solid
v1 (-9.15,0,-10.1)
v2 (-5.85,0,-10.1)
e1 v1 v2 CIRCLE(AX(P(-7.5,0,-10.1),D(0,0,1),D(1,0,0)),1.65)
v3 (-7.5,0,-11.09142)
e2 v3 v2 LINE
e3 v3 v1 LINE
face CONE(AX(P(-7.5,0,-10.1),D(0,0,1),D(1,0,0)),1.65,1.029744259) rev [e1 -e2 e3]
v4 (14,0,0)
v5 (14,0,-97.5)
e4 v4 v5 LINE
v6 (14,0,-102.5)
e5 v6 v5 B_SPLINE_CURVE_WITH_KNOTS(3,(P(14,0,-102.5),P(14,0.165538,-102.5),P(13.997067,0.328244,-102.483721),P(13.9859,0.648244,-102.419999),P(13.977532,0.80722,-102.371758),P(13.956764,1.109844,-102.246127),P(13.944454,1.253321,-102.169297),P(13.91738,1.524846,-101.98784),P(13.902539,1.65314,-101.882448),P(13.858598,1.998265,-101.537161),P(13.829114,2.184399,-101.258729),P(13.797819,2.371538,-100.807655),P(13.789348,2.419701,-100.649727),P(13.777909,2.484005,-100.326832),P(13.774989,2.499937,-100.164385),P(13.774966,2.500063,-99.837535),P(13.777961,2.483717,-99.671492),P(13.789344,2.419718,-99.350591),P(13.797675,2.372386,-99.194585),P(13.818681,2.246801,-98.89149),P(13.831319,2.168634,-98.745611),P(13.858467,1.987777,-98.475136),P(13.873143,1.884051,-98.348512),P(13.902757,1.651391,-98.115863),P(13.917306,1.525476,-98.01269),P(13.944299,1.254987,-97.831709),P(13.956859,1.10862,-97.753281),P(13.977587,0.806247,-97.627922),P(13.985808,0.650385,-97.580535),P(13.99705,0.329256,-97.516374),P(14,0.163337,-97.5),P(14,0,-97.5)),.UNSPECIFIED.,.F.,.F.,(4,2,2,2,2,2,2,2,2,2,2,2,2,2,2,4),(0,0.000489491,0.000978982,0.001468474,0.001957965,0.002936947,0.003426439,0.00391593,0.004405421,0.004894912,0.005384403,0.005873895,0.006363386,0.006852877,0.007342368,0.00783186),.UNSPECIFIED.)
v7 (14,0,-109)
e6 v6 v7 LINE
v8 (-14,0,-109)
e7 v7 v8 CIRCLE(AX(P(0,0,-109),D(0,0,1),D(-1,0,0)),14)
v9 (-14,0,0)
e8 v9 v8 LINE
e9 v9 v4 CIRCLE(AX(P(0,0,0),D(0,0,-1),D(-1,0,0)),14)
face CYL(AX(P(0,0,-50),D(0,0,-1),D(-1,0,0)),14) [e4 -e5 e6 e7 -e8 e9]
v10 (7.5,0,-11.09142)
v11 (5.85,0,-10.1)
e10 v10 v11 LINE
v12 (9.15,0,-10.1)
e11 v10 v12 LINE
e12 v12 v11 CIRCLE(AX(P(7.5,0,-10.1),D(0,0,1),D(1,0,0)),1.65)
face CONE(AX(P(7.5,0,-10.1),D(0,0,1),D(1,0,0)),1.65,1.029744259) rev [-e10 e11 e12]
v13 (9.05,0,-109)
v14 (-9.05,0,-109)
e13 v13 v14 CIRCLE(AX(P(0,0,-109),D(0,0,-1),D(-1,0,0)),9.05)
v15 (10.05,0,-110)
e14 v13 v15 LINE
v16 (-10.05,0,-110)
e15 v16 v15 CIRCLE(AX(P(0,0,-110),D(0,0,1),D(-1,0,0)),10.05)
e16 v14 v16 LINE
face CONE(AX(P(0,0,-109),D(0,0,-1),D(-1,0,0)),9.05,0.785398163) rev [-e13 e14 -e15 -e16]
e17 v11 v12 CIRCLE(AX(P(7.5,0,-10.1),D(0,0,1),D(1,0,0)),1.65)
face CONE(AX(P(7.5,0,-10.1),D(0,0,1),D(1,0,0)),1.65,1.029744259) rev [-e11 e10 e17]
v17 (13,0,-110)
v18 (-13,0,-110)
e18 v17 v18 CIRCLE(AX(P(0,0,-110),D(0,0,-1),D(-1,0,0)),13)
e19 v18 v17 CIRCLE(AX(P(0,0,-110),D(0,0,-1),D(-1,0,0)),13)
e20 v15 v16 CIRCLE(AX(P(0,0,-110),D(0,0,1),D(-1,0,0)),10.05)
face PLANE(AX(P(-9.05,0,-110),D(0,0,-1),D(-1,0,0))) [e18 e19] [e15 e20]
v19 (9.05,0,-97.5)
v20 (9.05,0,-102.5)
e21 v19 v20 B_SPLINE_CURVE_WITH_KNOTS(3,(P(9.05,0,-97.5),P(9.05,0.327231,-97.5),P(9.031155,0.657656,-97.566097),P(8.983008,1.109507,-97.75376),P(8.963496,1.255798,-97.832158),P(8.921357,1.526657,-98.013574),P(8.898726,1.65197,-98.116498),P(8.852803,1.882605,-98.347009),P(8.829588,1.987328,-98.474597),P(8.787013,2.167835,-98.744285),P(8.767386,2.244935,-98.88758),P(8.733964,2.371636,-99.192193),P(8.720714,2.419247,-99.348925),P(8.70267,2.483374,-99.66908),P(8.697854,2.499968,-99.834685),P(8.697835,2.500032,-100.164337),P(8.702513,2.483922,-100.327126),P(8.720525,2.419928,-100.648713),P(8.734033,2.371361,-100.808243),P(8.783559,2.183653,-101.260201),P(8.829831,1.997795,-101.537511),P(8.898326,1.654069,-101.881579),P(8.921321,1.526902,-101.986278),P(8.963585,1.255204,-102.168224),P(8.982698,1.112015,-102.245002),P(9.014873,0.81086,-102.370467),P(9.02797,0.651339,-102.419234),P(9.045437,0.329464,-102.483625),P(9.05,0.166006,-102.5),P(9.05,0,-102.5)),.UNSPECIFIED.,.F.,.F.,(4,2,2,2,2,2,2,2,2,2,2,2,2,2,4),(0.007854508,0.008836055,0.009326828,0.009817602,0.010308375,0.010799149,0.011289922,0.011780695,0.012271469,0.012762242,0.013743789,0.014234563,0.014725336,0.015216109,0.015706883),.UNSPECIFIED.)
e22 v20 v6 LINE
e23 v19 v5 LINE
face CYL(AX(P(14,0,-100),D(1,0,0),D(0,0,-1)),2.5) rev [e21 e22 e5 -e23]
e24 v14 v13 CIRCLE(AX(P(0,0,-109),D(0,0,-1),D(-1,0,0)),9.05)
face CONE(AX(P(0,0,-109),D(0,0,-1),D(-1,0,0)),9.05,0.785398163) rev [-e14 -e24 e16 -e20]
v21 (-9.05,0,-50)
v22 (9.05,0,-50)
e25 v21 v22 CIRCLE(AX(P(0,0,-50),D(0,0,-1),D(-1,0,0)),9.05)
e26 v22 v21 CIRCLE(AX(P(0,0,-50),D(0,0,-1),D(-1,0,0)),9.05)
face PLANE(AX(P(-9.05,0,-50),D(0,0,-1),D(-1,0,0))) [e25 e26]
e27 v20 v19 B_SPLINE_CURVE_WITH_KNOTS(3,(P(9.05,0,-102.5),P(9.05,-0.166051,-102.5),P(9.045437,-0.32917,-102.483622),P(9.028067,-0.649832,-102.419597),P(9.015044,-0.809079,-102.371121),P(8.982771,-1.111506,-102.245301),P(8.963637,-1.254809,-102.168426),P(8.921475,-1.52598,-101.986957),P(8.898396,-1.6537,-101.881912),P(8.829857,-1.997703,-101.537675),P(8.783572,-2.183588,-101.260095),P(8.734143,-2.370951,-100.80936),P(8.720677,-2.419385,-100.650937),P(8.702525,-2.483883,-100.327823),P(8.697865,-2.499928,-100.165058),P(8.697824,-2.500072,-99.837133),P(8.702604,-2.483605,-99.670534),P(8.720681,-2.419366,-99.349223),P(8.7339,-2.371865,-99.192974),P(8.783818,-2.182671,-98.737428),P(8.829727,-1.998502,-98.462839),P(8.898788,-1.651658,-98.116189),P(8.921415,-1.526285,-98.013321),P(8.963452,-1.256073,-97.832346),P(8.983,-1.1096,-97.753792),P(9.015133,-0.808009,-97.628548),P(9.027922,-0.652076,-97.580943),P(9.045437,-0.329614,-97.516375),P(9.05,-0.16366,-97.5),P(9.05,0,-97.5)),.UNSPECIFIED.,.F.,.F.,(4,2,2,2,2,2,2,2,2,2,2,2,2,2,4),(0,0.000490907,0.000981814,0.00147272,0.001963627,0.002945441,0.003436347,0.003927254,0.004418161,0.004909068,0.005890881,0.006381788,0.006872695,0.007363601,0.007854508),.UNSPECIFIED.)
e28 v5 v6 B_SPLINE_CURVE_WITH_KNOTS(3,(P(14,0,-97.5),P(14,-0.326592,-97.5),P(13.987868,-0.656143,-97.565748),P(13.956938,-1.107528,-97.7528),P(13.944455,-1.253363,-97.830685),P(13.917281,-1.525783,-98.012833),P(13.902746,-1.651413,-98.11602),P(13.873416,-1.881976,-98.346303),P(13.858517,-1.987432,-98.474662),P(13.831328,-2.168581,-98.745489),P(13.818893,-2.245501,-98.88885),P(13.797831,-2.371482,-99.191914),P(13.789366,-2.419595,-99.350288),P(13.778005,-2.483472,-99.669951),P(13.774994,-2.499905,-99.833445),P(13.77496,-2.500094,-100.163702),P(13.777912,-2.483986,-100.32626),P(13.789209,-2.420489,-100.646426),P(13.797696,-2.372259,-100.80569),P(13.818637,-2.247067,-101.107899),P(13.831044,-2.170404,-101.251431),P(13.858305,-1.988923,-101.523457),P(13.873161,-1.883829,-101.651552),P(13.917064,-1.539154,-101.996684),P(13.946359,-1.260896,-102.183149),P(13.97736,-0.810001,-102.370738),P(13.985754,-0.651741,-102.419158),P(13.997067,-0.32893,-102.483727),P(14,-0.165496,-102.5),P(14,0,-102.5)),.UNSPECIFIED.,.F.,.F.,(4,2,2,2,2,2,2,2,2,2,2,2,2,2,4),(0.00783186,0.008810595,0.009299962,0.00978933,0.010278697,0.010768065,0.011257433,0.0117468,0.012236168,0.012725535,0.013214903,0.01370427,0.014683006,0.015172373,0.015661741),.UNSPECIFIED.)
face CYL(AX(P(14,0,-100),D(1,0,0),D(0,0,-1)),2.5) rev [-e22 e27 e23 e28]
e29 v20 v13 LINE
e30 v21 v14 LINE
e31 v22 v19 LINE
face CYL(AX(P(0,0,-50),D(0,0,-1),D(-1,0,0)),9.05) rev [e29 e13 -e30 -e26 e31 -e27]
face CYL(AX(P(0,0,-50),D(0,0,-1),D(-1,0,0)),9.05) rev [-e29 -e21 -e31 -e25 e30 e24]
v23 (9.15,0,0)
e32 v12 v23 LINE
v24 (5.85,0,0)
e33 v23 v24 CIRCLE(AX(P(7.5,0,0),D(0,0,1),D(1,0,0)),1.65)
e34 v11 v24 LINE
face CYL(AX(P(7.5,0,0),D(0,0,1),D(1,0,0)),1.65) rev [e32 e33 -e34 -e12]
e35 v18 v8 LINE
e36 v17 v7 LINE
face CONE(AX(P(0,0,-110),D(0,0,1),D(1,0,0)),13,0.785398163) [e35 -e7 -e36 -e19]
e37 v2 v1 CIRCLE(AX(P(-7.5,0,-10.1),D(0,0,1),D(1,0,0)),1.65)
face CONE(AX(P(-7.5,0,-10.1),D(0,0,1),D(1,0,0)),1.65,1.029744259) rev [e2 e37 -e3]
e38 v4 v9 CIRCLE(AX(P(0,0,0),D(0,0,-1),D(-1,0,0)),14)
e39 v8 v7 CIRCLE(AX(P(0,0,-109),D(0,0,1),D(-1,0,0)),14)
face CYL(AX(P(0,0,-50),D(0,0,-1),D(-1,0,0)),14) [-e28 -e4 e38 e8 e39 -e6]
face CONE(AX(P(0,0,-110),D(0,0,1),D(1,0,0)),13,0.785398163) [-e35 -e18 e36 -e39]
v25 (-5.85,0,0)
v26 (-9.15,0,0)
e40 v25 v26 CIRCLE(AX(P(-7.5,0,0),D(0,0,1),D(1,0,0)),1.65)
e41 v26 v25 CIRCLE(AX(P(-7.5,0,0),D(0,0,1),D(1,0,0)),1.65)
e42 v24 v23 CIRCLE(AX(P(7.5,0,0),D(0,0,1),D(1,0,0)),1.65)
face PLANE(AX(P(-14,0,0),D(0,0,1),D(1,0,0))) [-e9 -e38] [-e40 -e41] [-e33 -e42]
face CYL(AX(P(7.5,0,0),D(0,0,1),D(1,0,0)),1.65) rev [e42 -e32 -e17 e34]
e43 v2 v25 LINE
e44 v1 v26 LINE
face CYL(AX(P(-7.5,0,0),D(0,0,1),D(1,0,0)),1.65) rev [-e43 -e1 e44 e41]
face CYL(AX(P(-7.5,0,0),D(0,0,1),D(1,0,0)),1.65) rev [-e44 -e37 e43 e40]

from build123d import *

# Parameters (mm, degrees)
M4_TAPPED_HOLE1_D     = 3.3
M4_TAPPED_HOLE1_DEPTH = 10.1
M4_TAPPED_HOLE1_TIP   = 0.991420021
M6_TAPPED_HOLE1_D     = 5
M6_TAPPED_HOLE1_DEPTH = 17
M6_TAPPED_HOLE1_TIP   = 1.502151548
CHAMFER1_SIZE         = 1


with BuildPart() as part:
    # Sketch1 → Revolve1 (revolve)
    with BuildSketch(Plane(origin=(0, 0, 0), x_dir=(1, 0, 0), z_dir=(0, 1, 0))):
        Polygon((-9.05, 110), (-14, 110), (-14, 0), (0, 0), (0, 50), (-9.05, 50), align=None)
    revolve(axis=Axis((0, 0, -50), (0, 0, 1)))

    # M4 Tapped Hole1
    with Locations(Plane(origin=(-7.5, 0, 0), x_dir=(1, 0, 0), z_dir=(0, 0, 1))):
        with Locations((0, 0), (15, 0)):
            Hole(M4_TAPPED_HOLE1_D / 2, depth=M4_TAPPED_HOLE1_DEPTH)
            with Locations((0, 0, -(M4_TAPPED_HOLE1_DEPTH + M4_TAPPED_HOLE1_TIP / 2))):  # 118° drill point
                Cone(0, M4_TAPPED_HOLE1_D / 2, M4_TAPPED_HOLE1_TIP, mode=Mode.SUBTRACT)

    # M6 Tapped Hole1
    with Locations(Plane(origin=(14, 0, -100), x_dir=(0, 1, 0), z_dir=(1, 0, 0))):
        with Locations((0, 0)):
            Hole(M6_TAPPED_HOLE1_D / 2, depth=M6_TAPPED_HOLE1_DEPTH)
            with Locations((0, 0, -(M6_TAPPED_HOLE1_DEPTH + M6_TAPPED_HOLE1_TIP / 2))):  # 118° drill point
                Cone(0, M6_TAPPED_HOLE1_D / 2, M6_TAPPED_HOLE1_TIP, mode=Mode.SUBTRACT)

    # Chamfer1
    chamfer1_edges = [part.edges().sort_by_distance(p)[0] for p in [
        (14, 0, -110),
        (9.05, 0, -110),
    ]]
    chamfer(chamfer1_edges, length=CHAMFER1_SIZE)


solid = part.part
